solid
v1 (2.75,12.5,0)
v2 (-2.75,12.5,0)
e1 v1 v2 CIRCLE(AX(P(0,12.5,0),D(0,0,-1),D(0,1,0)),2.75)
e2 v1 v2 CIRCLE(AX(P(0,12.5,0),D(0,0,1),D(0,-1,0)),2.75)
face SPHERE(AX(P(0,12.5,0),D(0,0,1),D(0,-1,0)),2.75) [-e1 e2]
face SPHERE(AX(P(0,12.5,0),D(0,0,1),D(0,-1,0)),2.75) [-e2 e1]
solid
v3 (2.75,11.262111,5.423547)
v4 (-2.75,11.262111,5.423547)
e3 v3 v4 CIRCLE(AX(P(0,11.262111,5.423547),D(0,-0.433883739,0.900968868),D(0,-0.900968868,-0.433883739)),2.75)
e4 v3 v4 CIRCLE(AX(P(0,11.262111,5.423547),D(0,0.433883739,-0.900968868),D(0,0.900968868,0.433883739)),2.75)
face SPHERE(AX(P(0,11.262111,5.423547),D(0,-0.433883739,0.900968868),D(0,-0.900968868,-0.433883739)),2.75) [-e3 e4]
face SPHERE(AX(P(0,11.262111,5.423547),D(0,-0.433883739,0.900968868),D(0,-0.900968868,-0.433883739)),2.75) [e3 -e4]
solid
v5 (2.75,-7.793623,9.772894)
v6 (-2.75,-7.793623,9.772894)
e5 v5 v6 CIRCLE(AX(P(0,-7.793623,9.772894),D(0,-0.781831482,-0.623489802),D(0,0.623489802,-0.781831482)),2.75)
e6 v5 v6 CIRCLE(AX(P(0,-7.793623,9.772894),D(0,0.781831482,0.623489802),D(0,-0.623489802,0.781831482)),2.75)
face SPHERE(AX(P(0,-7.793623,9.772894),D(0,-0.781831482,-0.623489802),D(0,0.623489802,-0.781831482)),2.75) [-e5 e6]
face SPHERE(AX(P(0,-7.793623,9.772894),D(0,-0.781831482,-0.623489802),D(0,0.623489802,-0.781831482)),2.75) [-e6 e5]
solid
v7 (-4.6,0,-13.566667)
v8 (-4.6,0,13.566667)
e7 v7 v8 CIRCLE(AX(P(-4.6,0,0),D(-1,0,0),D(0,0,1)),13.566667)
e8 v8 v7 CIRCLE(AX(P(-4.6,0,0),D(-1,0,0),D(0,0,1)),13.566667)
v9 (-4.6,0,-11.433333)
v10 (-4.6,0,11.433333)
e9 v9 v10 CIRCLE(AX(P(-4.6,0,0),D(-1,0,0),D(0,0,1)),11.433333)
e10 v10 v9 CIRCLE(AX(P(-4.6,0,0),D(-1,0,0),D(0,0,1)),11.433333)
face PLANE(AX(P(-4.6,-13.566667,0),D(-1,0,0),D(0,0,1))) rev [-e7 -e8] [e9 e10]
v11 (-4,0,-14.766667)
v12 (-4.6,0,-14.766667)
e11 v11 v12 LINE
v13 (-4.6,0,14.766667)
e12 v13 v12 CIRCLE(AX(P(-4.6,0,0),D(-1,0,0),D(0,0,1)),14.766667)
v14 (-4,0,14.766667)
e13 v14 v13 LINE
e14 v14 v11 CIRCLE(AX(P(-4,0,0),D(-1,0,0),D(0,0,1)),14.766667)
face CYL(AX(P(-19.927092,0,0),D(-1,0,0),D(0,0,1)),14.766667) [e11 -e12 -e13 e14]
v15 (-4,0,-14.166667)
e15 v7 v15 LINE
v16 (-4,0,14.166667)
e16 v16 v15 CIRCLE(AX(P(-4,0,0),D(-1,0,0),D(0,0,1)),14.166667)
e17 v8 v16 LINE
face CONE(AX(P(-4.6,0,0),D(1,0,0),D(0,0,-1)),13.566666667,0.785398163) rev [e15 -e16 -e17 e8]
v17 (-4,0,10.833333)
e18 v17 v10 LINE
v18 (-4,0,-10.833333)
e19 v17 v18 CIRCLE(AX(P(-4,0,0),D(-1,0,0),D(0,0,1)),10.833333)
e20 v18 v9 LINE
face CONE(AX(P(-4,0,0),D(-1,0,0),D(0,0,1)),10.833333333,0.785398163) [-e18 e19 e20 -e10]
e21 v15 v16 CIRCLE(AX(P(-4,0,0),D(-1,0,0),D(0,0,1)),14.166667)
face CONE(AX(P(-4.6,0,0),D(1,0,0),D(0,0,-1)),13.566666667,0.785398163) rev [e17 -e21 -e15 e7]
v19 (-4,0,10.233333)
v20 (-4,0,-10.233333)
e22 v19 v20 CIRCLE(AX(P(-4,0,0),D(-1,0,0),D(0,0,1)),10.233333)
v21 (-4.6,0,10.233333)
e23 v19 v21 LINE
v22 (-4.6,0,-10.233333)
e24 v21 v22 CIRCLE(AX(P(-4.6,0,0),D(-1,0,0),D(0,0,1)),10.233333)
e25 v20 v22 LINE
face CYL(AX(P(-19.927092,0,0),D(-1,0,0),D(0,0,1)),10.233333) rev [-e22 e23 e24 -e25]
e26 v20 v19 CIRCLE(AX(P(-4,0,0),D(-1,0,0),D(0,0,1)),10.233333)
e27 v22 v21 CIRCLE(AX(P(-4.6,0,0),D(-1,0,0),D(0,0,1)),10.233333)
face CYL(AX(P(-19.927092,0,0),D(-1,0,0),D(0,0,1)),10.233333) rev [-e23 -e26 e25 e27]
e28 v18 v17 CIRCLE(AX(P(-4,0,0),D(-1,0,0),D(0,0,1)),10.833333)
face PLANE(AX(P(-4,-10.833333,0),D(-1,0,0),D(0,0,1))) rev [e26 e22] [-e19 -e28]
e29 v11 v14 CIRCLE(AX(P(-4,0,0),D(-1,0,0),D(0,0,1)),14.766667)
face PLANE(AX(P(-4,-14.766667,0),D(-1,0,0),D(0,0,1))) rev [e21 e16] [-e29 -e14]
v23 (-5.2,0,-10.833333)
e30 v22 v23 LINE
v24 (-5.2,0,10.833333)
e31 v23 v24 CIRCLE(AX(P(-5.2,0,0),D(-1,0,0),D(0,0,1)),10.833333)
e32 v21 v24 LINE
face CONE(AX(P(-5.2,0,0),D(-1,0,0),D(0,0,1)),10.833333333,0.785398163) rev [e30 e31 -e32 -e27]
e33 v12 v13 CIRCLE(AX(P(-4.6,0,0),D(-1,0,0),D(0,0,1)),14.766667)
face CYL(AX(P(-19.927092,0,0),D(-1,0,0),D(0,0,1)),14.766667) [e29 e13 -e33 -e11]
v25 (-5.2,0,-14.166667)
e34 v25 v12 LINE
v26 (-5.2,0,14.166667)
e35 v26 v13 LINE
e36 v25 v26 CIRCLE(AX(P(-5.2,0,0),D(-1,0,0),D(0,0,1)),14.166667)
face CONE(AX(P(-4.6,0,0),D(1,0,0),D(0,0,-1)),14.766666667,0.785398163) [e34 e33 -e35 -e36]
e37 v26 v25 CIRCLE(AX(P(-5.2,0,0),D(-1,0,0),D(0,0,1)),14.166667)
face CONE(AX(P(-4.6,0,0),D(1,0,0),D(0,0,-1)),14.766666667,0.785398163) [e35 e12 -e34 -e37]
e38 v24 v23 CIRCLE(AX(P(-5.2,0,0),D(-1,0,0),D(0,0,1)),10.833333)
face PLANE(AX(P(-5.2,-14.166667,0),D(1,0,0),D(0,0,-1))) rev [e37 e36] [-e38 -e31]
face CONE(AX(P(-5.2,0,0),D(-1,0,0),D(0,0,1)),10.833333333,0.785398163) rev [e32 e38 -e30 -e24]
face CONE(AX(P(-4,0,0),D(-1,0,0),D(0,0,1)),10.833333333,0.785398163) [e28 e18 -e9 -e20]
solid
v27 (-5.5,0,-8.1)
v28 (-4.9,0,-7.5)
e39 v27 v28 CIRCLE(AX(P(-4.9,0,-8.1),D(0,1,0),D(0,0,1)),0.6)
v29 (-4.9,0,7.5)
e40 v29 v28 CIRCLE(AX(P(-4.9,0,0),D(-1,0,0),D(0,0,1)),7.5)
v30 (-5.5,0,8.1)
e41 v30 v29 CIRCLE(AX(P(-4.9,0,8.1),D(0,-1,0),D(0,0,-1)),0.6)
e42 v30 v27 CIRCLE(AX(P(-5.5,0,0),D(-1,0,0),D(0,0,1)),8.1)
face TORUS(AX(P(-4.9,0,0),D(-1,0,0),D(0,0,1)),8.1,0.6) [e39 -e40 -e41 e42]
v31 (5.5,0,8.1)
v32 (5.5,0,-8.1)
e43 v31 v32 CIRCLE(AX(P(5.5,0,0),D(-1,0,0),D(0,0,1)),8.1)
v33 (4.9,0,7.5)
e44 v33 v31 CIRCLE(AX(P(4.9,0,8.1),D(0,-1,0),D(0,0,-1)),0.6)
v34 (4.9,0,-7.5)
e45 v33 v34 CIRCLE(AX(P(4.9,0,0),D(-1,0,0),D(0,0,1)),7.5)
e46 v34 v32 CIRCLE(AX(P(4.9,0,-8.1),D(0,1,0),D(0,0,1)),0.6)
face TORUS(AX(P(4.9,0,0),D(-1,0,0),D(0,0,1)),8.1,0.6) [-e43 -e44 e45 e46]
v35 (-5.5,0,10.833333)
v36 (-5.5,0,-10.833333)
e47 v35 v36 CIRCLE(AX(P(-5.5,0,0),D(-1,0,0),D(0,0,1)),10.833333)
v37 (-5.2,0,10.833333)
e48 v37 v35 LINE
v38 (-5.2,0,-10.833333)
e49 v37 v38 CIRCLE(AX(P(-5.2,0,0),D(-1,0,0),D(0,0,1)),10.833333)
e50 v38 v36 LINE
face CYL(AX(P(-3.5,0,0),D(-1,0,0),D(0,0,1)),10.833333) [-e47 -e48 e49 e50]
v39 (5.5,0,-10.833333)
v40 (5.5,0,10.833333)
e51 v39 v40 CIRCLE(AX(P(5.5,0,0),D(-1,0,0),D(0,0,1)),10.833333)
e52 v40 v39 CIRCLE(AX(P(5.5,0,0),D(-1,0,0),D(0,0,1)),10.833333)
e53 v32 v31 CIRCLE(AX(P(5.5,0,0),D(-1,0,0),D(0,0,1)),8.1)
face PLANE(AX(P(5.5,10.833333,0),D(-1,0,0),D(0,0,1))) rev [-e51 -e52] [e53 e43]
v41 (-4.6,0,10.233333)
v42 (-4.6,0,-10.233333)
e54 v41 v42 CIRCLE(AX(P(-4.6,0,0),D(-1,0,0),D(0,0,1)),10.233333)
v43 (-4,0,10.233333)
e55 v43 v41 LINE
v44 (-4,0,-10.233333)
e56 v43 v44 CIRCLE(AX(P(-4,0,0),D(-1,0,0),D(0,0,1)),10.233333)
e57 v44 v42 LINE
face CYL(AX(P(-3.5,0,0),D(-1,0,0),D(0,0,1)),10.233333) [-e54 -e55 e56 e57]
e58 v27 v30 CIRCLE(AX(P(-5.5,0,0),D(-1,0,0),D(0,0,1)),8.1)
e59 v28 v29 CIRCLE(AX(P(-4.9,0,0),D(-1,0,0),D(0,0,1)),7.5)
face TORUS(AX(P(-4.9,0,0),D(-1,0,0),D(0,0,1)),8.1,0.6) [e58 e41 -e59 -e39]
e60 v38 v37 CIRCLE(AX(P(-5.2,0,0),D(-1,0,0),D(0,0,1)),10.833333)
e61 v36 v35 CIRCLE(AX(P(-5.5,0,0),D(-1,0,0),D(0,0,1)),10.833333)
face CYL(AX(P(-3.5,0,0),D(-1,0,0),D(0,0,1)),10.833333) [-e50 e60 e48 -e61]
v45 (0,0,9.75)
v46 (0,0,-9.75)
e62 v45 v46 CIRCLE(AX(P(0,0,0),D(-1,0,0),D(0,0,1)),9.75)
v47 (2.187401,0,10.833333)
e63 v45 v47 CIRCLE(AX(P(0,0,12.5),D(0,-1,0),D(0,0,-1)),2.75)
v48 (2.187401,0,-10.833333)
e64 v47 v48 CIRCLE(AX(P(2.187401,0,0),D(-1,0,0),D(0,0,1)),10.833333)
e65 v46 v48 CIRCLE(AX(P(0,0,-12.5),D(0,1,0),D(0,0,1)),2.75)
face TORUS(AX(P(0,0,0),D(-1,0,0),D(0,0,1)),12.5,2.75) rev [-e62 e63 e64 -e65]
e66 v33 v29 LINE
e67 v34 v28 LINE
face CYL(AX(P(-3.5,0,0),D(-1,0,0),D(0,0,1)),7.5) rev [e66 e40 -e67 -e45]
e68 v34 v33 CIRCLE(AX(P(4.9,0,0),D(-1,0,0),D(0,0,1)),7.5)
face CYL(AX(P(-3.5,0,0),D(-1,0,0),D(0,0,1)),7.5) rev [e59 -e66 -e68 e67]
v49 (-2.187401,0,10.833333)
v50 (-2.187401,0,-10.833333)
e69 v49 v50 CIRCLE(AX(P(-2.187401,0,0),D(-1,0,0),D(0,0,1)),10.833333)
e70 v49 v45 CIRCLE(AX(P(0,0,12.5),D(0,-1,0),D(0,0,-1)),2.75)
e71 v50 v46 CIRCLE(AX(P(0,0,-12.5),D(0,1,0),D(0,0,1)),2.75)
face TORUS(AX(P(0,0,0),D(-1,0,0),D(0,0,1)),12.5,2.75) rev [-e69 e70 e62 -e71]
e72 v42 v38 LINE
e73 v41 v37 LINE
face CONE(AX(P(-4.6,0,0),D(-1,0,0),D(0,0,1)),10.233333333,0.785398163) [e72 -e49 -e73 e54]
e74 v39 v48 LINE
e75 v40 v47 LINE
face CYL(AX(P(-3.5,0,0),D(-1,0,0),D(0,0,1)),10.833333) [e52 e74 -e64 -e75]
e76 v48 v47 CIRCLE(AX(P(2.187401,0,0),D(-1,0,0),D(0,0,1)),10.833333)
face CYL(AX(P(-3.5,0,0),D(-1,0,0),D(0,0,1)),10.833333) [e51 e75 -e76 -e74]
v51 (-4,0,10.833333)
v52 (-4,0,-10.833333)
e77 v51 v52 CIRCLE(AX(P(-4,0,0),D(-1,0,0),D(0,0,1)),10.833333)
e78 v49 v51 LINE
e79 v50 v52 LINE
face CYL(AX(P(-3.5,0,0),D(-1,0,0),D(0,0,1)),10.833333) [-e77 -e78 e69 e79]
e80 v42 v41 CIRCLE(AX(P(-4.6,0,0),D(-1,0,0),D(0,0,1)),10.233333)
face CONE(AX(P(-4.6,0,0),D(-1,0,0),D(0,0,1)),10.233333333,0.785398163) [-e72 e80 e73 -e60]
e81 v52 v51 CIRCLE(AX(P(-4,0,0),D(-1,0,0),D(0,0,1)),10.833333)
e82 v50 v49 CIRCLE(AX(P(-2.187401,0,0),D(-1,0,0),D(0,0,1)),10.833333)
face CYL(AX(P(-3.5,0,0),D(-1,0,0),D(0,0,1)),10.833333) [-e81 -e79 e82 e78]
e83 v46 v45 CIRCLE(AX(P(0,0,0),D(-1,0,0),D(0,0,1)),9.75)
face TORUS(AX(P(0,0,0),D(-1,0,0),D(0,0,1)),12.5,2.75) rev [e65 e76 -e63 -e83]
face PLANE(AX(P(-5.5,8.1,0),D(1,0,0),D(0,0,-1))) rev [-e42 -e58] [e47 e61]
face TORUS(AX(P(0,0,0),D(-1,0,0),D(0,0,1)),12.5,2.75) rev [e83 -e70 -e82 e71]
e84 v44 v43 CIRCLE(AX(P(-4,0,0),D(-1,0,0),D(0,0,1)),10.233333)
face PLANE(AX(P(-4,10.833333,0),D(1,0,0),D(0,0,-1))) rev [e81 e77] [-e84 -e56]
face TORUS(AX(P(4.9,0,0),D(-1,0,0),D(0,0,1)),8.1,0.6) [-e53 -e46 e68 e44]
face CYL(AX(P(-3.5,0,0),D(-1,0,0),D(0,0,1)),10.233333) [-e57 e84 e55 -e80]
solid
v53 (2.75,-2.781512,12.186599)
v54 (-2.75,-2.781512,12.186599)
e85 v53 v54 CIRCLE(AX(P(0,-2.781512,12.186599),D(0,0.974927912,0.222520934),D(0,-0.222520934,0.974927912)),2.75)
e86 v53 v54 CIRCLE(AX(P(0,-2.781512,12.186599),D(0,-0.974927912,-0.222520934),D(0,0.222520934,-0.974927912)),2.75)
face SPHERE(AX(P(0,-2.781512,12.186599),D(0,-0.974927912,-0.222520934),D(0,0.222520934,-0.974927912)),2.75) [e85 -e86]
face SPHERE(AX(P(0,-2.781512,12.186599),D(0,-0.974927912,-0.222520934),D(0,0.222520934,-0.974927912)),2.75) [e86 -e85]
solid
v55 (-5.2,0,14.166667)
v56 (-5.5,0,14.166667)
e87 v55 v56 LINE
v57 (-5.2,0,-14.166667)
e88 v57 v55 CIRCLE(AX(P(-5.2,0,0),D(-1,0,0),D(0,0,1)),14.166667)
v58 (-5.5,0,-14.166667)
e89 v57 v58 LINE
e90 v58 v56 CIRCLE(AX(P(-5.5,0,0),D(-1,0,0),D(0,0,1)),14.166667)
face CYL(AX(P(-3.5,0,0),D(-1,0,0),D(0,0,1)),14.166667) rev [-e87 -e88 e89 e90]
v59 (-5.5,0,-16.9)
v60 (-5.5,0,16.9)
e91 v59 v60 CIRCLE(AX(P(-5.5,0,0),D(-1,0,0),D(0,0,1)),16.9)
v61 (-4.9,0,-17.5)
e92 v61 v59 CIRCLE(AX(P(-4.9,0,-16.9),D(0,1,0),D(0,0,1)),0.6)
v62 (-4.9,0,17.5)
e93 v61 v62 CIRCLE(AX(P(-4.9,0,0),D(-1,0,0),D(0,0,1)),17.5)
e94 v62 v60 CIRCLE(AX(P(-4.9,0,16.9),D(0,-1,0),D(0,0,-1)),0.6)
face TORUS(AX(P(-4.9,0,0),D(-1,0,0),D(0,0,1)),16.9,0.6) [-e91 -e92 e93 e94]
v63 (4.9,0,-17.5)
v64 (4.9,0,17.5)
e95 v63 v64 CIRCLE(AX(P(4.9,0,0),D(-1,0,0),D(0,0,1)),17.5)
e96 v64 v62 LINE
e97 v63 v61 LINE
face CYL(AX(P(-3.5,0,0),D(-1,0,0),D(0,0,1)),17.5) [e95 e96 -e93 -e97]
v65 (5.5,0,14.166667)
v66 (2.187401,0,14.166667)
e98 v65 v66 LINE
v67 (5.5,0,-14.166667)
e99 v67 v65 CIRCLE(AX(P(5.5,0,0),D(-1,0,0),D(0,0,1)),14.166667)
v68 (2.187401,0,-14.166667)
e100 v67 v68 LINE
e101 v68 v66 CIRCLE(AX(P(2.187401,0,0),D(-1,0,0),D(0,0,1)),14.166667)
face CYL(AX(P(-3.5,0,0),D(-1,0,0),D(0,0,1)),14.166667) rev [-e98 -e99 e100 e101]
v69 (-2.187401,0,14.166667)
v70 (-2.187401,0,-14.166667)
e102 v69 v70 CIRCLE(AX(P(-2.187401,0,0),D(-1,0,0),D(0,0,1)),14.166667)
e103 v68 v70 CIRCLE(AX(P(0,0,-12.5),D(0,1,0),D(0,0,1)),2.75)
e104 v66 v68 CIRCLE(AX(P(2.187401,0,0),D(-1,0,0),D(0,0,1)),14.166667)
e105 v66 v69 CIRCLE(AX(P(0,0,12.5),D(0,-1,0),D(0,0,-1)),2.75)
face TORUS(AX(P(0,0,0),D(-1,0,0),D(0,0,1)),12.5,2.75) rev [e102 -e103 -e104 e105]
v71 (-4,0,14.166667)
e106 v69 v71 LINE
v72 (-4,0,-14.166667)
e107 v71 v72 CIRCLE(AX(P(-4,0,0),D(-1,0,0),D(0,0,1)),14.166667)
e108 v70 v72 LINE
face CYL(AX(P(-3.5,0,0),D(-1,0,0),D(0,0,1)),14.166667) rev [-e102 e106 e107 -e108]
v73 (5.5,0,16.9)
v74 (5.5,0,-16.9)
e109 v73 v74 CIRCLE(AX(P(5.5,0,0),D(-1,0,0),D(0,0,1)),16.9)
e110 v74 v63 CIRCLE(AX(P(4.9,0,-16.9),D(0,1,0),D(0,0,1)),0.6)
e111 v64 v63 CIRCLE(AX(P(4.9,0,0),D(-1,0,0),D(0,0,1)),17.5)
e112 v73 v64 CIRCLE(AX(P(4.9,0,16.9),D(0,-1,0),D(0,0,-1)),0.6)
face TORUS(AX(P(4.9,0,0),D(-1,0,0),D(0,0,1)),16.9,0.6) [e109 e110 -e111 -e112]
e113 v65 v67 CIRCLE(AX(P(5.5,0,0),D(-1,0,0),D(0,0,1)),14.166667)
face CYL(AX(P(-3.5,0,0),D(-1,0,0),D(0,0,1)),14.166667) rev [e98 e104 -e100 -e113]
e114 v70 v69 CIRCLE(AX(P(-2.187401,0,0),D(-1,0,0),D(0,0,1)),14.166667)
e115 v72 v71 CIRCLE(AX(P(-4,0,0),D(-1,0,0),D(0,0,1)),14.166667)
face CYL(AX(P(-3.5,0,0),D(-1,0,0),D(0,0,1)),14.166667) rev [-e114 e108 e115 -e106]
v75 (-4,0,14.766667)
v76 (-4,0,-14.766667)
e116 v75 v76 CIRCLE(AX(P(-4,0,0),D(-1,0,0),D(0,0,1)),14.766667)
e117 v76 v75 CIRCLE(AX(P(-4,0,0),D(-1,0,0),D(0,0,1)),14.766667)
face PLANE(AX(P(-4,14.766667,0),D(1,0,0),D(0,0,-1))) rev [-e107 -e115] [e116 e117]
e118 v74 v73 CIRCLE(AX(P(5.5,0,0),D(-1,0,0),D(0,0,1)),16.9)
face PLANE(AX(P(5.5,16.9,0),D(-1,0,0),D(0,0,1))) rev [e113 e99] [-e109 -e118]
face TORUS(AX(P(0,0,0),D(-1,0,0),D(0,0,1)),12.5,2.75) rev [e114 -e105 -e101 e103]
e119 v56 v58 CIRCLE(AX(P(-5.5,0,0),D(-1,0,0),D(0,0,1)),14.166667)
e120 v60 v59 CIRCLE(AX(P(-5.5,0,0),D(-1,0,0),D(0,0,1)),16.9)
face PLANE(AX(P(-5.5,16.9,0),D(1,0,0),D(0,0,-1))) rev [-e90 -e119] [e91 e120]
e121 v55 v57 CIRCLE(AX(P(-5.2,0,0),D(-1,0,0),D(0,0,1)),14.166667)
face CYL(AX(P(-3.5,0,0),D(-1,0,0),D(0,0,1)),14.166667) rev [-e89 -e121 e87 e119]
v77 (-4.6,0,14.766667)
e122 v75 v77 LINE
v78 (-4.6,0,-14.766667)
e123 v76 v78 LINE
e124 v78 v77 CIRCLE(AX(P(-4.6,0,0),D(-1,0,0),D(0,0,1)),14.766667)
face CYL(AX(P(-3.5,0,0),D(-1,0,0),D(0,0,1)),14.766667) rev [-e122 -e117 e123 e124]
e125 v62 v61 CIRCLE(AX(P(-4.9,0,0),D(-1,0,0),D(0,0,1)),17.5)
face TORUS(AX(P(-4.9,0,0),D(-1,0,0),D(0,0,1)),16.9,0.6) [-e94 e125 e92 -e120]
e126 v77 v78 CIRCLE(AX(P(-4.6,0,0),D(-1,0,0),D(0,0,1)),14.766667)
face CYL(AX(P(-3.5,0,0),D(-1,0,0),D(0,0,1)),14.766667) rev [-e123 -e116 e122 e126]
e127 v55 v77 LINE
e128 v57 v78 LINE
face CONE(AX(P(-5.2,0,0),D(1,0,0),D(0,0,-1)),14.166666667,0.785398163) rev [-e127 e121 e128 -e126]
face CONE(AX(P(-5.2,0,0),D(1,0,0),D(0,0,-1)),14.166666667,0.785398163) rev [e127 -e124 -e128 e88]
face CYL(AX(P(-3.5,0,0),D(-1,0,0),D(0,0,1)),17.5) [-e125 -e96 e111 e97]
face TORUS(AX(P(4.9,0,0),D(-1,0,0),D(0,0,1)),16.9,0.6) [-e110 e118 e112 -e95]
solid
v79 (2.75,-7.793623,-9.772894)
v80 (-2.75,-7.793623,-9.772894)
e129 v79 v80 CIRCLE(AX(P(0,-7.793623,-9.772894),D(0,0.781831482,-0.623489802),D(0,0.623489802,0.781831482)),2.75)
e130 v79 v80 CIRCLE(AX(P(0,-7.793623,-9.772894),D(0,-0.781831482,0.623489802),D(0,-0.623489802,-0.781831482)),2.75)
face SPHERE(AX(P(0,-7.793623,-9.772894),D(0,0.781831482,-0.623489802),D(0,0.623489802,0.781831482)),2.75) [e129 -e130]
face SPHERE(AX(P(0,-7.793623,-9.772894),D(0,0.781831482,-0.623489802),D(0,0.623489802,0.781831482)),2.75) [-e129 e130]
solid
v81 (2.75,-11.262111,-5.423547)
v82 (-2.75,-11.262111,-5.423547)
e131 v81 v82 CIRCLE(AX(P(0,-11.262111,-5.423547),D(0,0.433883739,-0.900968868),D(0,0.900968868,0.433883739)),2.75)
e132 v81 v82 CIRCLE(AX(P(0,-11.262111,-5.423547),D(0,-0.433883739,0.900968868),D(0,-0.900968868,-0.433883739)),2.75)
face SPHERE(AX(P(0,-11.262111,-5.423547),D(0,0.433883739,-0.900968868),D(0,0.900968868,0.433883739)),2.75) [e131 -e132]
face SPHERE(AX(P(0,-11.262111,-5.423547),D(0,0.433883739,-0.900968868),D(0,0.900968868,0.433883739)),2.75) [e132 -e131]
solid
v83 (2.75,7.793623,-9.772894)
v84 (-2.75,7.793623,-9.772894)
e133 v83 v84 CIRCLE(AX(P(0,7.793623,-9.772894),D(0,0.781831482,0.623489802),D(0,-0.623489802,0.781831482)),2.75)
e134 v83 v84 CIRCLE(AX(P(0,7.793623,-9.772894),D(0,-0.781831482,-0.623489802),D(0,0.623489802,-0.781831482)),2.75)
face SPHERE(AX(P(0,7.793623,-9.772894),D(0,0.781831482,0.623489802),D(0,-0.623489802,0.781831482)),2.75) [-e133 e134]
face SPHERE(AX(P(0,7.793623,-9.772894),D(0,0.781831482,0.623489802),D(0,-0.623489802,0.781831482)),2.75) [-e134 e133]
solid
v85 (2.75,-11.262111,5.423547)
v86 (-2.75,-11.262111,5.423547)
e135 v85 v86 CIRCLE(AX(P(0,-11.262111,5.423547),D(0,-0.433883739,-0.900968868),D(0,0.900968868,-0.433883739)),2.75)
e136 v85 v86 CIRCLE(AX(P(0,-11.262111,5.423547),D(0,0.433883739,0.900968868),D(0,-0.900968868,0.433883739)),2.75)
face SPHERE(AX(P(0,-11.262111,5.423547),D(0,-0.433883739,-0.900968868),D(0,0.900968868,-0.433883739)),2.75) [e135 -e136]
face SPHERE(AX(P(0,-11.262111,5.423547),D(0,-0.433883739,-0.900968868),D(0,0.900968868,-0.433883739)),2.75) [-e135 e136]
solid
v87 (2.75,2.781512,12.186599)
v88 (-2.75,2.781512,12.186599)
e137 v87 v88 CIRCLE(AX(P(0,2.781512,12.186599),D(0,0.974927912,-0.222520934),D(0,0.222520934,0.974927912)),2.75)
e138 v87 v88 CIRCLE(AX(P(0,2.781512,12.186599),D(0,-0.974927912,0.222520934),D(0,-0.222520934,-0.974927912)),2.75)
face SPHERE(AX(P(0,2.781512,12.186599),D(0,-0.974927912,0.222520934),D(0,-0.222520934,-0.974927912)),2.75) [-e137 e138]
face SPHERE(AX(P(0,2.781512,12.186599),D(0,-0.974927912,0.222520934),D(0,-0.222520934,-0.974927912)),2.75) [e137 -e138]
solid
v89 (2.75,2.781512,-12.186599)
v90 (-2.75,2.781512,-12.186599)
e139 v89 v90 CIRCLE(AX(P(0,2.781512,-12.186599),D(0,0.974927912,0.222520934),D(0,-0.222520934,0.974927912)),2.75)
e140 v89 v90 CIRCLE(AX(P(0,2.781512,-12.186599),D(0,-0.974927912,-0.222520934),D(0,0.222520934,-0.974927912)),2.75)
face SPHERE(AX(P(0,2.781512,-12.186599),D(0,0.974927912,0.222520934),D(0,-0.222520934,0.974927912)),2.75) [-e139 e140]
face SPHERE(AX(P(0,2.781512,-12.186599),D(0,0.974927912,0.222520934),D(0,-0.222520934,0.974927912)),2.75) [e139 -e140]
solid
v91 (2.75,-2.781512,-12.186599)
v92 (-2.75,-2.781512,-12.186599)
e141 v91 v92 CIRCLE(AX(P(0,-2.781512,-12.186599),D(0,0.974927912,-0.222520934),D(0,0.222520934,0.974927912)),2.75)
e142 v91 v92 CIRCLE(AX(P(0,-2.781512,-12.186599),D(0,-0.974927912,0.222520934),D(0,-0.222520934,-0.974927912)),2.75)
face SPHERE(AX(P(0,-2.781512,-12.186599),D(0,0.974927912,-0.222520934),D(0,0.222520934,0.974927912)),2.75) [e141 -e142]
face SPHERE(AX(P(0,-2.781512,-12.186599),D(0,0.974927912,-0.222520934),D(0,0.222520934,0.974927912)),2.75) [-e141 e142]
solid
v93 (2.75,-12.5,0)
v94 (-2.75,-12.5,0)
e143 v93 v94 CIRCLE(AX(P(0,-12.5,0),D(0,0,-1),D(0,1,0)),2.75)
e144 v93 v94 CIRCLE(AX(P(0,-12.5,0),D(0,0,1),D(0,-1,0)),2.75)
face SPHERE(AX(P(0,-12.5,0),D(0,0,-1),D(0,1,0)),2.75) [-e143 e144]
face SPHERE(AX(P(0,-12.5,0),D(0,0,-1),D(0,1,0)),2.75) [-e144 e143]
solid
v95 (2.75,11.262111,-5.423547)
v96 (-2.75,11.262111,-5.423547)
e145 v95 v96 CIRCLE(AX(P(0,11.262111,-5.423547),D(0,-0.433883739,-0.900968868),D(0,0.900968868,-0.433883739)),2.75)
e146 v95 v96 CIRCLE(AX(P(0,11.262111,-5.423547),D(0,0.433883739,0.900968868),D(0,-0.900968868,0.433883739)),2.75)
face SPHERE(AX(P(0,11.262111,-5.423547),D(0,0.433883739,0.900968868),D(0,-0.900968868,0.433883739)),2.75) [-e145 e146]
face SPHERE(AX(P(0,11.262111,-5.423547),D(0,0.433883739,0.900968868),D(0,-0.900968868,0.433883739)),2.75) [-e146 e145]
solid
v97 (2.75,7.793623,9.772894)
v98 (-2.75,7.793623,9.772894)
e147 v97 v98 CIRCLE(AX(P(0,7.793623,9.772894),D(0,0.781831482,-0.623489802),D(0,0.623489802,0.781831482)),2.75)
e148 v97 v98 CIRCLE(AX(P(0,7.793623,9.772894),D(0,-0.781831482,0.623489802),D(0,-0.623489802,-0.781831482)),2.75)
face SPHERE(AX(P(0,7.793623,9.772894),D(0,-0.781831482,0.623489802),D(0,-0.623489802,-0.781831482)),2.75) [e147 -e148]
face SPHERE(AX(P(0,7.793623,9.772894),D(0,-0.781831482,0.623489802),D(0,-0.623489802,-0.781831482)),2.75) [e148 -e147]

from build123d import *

# Parameters (mm, degrees)
PATTERN_CIRCULAR_5_COUNT = 14


with BuildPart() as part:
    # 草图2 → 旋转1 (revolve)
    with BuildSketch(Plane.XY, mode=Mode.PRIVATE) as revolve_1_sk:
        with BuildLine():
            Line((-5.2, 10.833333333), (-5.5, 10.833333333))
            Line((-5.5, 10.833333333), (-5.5, 10.233333333))
            Line((-5.5, 10.233333333), (-5.5, 8.1))
            ThreePointArc((-5.5, 8.1), (-5.324264069, 7.675735931), (-4.9, 7.5))
            Line((-4.9, 7.5), (4.9, 7.5))
            ThreePointArc((4.9, 7.5), (5.324264069, 7.675735931), (5.5, 8.1))
            Line((5.5, 8.1), (5.5, 10.233333333))
            Line((5.5, 10.233333333), (5.5, 10.833333333))
            Line((5.5, 10.833333333), (4.9, 10.833333333))
            Line((4.9, 10.833333333), (2.187400791, 10.833333333))
            ThreePointArc((2.187400791, 10.833333333), (0, 9.75), (-2.187400791, 10.833333333))
            Line((-2.187400791, 10.833333333), (-4, 10.833333333))
            Line((-4, 10.833333333), (-4, 10.233333333))
            Line((-4, 10.233333333), (-4.6, 10.233333333))
            Line((-4.6, 10.233333333), (-5.2, 10.833333333))
        make_face()
        with BuildLine():
            Line((-5.5, 14.166666667), (-5.2, 14.166666667))
            Line((-5.2, 14.166666667), (-4.6, 14.766666667))
            Line((-4.6, 14.766666667), (-4, 14.766666667))
            Line((-4, 14.766666667), (-4, 14.166666667))
            Line((-4, 14.166666667), (-2.187400791, 14.166666667))
            ThreePointArc((-2.187400791, 14.166666667), (0, 15.25), (2.187400791, 14.166666667))
            Line((2.187400791, 14.166666667), (5.5, 14.166666667))
            Line((5.5, 14.166666667), (5.5, 16.9))
            ThreePointArc((5.5, 16.9), (5.324264069, 17.324264069), (4.9, 17.5))
            Line((4.9, 17.5), (-4.9, 17.5))
            ThreePointArc((-4.9, 17.5), (-5.324264069, 17.324264069), (-5.5, 16.9))
            Line((-5.5, 16.9), (-5.5, 14.166666667))
        make_face()
    revolve(revolve_1_sk.sketch.rotate(Axis((-3.5, 0, 0), (1, 0, 0)), 90), axis=Axis((-3.5, 0, 0), (1, 0, 0)))


with BuildPart() as body_2:
    # 草图3 → 旋转2 (revolve)
    with BuildSketch(Plane.XY):
        with BuildLine():
            Line((-2.75, 12.5), (2.75, 12.5))
            ThreePointArc((2.75, 12.5), (0, 15.25), (-2.75, 12.5))
        make_face()
    revolve(axis=Axis((2.75, 12.5, 0), (1, 0, 0)))


with BuildPart() as body_3:
    # 草图4 → 旋转3 (revolve)
    with BuildSketch(Plane.XY, mode=Mode.PRIVATE) as revolve_3_sk:
        Polygon((-5.2, 14.166666667), (-5.2, 10.833333333), (-4.6, 10.233333333), (-4, 10.233333333), (-4, 10.833333333), (-4.6, 11.433333333), (-4.6, 13.566666667), (-4, 14.166666667), (-4, 14.766666667), (-4.6, 14.766666667), align=None)
    revolve(revolve_3_sk.sketch.rotate(Axis((-19.927092192, 0, 0), (1, 0, 0)), 90), axis=Axis((-19.927092192, 0, 0), (1, 0, 0)))


with BuildPart() as pattern_circular_5_1:
    # 阵列(圆周)5: pattern copy
    add(body_2.part.rotate(Axis((0, 0, 0), (1, 0, 0)), 1 * 360 / PATTERN_CIRCULAR_5_COUNT))


with BuildPart() as pattern_circular_5_2:
    # 阵列(圆周)5: pattern copy
    add(body_2.part.rotate(Axis((0, 0, 0), (1, 0, 0)), 2 * 360 / PATTERN_CIRCULAR_5_COUNT))


with BuildPart() as pattern_circular_5_3:
    # 阵列(圆周)5: pattern copy
    add(body_2.part.rotate(Axis((0, 0, 0), (1, 0, 0)), 3 * 360 / PATTERN_CIRCULAR_5_COUNT))


with BuildPart() as pattern_circular_5_4:
    # 阵列(圆周)5: pattern copy
    add(body_2.part.rotate(Axis((0, 0, 0), (1, 0, 0)), 4 * 360 / PATTERN_CIRCULAR_5_COUNT))


with BuildPart() as pattern_circular_5_5:
    # 阵列(圆周)5: pattern copy
    add(body_2.part.rotate(Axis((0, 0, 0), (1, 0, 0)), 5 * 360 / PATTERN_CIRCULAR_5_COUNT))


with BuildPart() as pattern_circular_5_6:
    # 阵列(圆周)5: pattern copy
    add(body_2.part.rotate(Axis((0, 0, 0), (1, 0, 0)), 6 * 360 / PATTERN_CIRCULAR_5_COUNT))


with BuildPart() as pattern_circular_5_7:
    # 阵列(圆周)5: pattern copy
    add(body_2.part.rotate(Axis((0, 0, 0), (1, 0, 0)), 7 * 360 / PATTERN_CIRCULAR_5_COUNT))


with BuildPart() as pattern_circular_5_8:
    # 阵列(圆周)5: pattern copy
    add(body_2.part.rotate(Axis((0, 0, 0), (1, 0, 0)), 8 * 360 / PATTERN_CIRCULAR_5_COUNT))


with BuildPart() as pattern_circular_5_9:
    # 阵列(圆周)5: pattern copy
    add(body_2.part.rotate(Axis((0, 0, 0), (1, 0, 0)), 9 * 360 / PATTERN_CIRCULAR_5_COUNT))


with BuildPart() as pattern_circular_5_10:
    # 阵列(圆周)5: pattern copy
    add(body_2.part.rotate(Axis((0, 0, 0), (1, 0, 0)), 10 * 360 / PATTERN_CIRCULAR_5_COUNT))


with BuildPart() as pattern_circular_5_11:
    # 阵列(圆周)5: pattern copy
    add(body_2.part.rotate(Axis((0, 0, 0), (1, 0, 0)), 11 * 360 / PATTERN_CIRCULAR_5_COUNT))


with BuildPart() as pattern_circular_5_12:
    # 阵列(圆周)5: pattern copy
    add(body_2.part.rotate(Axis((0, 0, 0), (1, 0, 0)), 12 * 360 / PATTERN_CIRCULAR_5_COUNT))


with BuildPart() as pattern_circular_5_13:
    # 阵列(圆周)5: pattern copy
    add(body_2.part.rotate(Axis((0, 0, 0), (1, 0, 0)), 13 * 360 / PATTERN_CIRCULAR_5_COUNT))


solid = Compound([part.part, body_2.part, body_3.part, pattern_circular_5_1.part, pattern_circular_5_2.part, pattern_circular_5_3.part, pattern_circular_5_4.part, pattern_circular_5_5.part, pattern_circular_5_6.part, pattern_circular_5_7.part, pattern_circular_5_8.part, pattern_circular_5_9.part, pattern_circular_5_10.part, pattern_circular_5_11.part, pattern_circular_5_12.part, pattern_circular_5_13.part])
